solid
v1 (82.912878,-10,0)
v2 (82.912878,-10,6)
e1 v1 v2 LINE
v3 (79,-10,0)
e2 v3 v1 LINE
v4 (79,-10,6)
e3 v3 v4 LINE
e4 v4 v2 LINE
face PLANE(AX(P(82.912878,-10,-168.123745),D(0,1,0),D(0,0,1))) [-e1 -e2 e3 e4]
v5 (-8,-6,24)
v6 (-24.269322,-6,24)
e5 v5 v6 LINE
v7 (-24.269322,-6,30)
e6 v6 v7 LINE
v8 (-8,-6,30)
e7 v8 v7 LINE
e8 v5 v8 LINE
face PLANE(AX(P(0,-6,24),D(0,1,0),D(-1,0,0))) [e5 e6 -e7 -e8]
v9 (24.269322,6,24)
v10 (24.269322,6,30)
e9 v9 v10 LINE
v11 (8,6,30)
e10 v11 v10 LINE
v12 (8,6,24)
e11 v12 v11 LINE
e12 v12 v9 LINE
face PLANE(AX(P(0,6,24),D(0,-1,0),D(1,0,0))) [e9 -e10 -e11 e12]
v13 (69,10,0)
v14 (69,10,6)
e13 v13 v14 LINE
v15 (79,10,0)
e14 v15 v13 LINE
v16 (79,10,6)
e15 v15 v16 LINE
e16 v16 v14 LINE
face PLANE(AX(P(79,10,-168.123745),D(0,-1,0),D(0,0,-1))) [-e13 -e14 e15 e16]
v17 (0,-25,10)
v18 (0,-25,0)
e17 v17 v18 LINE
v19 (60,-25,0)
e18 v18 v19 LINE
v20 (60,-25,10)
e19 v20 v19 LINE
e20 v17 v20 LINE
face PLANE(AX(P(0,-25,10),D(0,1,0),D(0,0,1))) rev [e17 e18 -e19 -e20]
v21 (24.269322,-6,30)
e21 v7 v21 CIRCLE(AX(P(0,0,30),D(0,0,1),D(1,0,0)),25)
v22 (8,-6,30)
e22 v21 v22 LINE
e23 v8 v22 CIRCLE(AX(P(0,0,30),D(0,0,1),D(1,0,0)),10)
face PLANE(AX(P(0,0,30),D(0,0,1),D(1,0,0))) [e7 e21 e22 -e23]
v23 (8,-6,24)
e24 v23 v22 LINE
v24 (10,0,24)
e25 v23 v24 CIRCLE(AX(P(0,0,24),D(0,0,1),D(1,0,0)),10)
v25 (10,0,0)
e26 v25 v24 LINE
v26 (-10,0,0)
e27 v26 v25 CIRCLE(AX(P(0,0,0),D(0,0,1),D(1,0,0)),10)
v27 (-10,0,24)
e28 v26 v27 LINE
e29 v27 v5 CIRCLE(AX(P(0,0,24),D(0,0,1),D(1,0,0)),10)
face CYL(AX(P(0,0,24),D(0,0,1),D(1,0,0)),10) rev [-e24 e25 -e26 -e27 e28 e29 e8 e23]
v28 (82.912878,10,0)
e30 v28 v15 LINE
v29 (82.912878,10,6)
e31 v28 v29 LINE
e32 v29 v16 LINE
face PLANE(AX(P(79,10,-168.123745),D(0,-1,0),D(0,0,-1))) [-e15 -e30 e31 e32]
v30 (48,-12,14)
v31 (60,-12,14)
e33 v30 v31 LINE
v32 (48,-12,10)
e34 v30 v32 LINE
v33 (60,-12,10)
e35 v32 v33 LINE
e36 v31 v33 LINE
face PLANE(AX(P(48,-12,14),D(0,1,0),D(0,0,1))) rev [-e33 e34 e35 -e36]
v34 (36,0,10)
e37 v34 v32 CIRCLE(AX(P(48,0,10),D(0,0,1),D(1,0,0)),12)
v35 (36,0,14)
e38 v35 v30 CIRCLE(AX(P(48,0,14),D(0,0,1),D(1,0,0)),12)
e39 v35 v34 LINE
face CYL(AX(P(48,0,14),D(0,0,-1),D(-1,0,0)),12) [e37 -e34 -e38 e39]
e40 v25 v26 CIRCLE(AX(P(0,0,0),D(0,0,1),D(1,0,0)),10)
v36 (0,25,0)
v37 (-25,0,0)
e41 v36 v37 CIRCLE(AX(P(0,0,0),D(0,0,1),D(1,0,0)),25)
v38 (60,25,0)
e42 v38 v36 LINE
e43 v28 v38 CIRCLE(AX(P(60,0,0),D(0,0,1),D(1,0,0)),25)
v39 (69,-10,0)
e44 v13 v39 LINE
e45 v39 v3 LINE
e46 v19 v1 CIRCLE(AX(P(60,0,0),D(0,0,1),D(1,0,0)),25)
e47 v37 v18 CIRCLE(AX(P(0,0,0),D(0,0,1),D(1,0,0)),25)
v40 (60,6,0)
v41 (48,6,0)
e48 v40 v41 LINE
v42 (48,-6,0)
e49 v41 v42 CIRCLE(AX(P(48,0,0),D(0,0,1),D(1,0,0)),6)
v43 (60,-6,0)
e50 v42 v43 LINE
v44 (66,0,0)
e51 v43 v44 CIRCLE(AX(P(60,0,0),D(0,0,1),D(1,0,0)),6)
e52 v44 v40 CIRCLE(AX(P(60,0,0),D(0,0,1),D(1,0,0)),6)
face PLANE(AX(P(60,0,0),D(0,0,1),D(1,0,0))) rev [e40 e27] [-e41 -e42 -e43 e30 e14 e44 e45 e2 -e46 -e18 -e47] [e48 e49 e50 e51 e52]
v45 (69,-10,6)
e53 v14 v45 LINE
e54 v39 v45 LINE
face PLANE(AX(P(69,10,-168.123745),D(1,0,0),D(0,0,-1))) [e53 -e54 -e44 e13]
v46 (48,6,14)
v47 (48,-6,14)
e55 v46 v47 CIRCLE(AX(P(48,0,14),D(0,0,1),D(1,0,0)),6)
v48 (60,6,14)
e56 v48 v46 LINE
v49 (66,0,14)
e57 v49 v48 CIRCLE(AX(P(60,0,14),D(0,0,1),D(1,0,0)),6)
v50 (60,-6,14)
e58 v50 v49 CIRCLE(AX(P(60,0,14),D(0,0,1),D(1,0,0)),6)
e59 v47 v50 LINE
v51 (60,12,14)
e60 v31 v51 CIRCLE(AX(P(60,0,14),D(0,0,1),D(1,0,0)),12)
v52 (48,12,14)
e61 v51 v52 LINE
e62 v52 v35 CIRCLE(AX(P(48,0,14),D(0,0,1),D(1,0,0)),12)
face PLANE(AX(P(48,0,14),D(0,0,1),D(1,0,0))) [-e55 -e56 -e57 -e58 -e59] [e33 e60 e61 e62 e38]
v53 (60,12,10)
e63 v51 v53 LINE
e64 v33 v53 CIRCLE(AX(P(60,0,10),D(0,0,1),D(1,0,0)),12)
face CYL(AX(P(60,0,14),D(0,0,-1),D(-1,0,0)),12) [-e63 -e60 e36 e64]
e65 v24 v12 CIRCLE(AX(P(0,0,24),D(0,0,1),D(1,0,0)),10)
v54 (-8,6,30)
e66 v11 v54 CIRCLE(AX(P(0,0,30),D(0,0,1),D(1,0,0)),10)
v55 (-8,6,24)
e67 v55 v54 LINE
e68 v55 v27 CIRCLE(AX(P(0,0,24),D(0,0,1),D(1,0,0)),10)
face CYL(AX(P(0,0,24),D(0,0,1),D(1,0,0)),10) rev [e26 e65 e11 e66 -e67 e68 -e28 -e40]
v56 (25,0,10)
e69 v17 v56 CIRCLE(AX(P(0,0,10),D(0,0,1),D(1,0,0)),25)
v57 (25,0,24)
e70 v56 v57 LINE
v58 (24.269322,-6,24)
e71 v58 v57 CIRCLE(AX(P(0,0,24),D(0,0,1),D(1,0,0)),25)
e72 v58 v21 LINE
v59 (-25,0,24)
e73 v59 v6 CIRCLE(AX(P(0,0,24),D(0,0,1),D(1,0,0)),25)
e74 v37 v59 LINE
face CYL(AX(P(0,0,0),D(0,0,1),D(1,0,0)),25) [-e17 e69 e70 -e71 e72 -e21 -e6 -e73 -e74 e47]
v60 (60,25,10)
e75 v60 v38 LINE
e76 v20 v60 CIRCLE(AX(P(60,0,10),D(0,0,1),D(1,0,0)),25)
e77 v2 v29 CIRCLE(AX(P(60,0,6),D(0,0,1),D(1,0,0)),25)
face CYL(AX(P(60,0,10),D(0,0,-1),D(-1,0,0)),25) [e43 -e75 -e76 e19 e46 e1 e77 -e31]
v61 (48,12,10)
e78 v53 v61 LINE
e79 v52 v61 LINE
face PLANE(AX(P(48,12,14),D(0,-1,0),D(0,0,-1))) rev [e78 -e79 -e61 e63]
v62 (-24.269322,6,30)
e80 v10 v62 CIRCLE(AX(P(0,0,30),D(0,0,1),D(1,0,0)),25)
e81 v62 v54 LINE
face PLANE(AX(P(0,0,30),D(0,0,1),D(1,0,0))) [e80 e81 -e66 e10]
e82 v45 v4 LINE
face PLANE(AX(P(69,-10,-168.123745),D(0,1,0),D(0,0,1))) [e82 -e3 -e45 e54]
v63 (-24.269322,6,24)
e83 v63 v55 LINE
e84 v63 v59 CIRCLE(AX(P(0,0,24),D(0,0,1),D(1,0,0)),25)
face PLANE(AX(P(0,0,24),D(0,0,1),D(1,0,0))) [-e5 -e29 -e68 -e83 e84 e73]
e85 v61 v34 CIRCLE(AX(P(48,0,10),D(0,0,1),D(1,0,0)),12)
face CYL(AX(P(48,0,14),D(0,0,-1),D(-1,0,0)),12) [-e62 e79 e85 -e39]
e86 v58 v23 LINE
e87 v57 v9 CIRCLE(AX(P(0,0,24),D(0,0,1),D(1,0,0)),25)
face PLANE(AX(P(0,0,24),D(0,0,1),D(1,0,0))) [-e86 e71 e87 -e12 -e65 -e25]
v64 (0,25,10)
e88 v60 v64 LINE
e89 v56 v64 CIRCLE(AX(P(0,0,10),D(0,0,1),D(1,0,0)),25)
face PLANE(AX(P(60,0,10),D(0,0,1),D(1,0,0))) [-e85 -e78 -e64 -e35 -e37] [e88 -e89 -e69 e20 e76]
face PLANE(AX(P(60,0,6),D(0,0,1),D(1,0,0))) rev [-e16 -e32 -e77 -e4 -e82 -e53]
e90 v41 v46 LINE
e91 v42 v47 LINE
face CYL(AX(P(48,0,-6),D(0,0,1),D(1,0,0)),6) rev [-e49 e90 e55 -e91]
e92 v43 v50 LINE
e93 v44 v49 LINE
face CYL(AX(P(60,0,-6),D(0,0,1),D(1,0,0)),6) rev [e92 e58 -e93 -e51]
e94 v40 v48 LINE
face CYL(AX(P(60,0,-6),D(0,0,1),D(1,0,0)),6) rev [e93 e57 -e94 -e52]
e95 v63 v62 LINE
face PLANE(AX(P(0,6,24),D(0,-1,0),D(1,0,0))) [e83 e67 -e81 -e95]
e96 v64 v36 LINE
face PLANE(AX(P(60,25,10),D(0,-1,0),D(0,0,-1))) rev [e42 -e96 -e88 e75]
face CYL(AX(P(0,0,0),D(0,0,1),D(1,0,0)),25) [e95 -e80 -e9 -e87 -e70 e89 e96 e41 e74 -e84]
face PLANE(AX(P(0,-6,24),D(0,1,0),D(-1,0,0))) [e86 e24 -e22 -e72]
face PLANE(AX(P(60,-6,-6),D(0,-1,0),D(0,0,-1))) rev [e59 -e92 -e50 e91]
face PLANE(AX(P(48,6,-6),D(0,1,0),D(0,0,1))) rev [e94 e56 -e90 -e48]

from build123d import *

# Parameters (mm, degrees)
ARM_PLATE_DEPTH      = 10
HUB_FRONT_SKETCH_R   = 25
HUB_BOSS_FRONT_DEPTH = 10
HUB_START            = 20
HUB_BACK_SKETCH_R    = 25
HUB_BOSS_BACK_DEPTH  = 20
HUB_CROSS_SLOT_DEPTH = 6
BORE_SKETCH_R        = 10
BORE_20_DEPTH        = 30
SLOT_BOSS_DEPTH      = 4
ARM_SLOT_12MM_DEPTH  = 20
END_NOTCH_DEPTH      = 94.541434669
END_NOTCH_DEPTH_BACK = 6


with BuildPart() as part:
    # Arm Profile Sketch → Arm Plate (new body)
    with BuildSketch(Plane.XY):
        with BuildLine():
            Line((60, 25), (0, 25))
            Line((0, 25), (0, -25))
            Line((0, -25), (60, -25))
            ThreePointArc((60, -25), (85, 0), (60, 25))
        make_face()
    extrude(amount=ARM_PLATE_DEPTH)

    # Hub Front Sketch → Hub Boss Front (add)
    with BuildSketch(Plane.XY.offset(10)):
        Circle(HUB_FRONT_SKETCH_R)
    extrude(amount=-HUB_BOSS_FRONT_DEPTH)

    # Hub Back Sketch → Hub Boss Back (add)
    with BuildSketch(Plane.XY.offset(10).offset(HUB_START)):
        Circle(HUB_BACK_SKETCH_R)
    extrude(amount=-HUB_BOSS_BACK_DEPTH)

    # Hub Cross Slot Sketch → Hub Cross Slot (cut)
    with BuildSketch(Plane.XY.offset(30)):
        with BuildLine():
            ThreePointArc((24.269322199, -6), (24.816658266, -3.022163548), (25, 0))
            ThreePointArc((25, 0), (24.816658266, 3.022163548), (24.269322199, 6))
            Line((24.269322199, 6), (8, 6))
            ThreePointArc((8, 6), (0, 10), (-8, 6))
            Line((-8, 6), (-24.269322199, 6))
            ThreePointArc((-24.269322199, 6), (-24.816658266, 3.022163548), (-25, 0))
            ThreePointArc((-25, 0), (-24.816658266, -3.022163548), (-24.269322199, -6))
            Line((-24.269322199, -6), (-8, -6))
            ThreePointArc((-8, -6), (0, -10), (8, -6))
            Line((8, -6), (24.269322199, -6))
        make_face()
    extrude(amount=-HUB_CROSS_SLOT_DEPTH, mode=Mode.SUBTRACT)

    # Bore Sketch → Bore Ø20 (cut)
    with BuildSketch(Plane.XY.offset(24)):
        Circle(BORE_SKETCH_R)
    extrude(amount=-BORE_20_DEPTH, mode=Mode.SUBTRACT)

    # Slot Boss Sketch → Slot Boss (add)
    with BuildSketch(Plane.XY.offset(10)):
        with BuildLine():
            Line((48, 12), (60, 12))
            ThreePointArc((60, 12), (72, 0), (60, -12))
            Line((60, -12), (48, -12))
            ThreePointArc((48, -12), (36, 0), (48, 12))
        make_face()
    extrude(amount=SLOT_BOSS_DEPTH)

    # Arm Slot Sketch → Arm Slot 12mm (cut)
    with BuildSketch(Plane.XY.offset(14)):
        with BuildLine():
            Line((48, 6), (60, 6))
            ThreePointArc((60, 6), (66, 0), (60, -6))
            Line((60, -6), (48, -6))
            ThreePointArc((48, -6), (42, 0), (48, 6))
        make_face()
    extrude(amount=-ARM_SLOT_12MM_DEPTH, mode=Mode.SUBTRACT)

    # End Notch Sketch → End Notch (cut, two sides: drawn at the far end of the back side and taken through both)
    with BuildSketch(Plane(origin=(0, 0, 0), x_dir=(-1, 0, 0), z_dir=(0, 0, -1)).offset(-END_NOTCH_DEPTH_BACK)):
        Polygon((-319.806592277, -10), (-82.912878475, -10), (-79, -10), (-69, -10), (-69, 10), (-79, 10), (-82.912878475, 10), (-319.806592277, 10), (-793.594019881, 10), (-793.594019881, -10), align=None)
    extrude(amount=END_NOTCH_DEPTH + END_NOTCH_DEPTH_BACK, mode=Mode.SUBTRACT)


solid = part.part
